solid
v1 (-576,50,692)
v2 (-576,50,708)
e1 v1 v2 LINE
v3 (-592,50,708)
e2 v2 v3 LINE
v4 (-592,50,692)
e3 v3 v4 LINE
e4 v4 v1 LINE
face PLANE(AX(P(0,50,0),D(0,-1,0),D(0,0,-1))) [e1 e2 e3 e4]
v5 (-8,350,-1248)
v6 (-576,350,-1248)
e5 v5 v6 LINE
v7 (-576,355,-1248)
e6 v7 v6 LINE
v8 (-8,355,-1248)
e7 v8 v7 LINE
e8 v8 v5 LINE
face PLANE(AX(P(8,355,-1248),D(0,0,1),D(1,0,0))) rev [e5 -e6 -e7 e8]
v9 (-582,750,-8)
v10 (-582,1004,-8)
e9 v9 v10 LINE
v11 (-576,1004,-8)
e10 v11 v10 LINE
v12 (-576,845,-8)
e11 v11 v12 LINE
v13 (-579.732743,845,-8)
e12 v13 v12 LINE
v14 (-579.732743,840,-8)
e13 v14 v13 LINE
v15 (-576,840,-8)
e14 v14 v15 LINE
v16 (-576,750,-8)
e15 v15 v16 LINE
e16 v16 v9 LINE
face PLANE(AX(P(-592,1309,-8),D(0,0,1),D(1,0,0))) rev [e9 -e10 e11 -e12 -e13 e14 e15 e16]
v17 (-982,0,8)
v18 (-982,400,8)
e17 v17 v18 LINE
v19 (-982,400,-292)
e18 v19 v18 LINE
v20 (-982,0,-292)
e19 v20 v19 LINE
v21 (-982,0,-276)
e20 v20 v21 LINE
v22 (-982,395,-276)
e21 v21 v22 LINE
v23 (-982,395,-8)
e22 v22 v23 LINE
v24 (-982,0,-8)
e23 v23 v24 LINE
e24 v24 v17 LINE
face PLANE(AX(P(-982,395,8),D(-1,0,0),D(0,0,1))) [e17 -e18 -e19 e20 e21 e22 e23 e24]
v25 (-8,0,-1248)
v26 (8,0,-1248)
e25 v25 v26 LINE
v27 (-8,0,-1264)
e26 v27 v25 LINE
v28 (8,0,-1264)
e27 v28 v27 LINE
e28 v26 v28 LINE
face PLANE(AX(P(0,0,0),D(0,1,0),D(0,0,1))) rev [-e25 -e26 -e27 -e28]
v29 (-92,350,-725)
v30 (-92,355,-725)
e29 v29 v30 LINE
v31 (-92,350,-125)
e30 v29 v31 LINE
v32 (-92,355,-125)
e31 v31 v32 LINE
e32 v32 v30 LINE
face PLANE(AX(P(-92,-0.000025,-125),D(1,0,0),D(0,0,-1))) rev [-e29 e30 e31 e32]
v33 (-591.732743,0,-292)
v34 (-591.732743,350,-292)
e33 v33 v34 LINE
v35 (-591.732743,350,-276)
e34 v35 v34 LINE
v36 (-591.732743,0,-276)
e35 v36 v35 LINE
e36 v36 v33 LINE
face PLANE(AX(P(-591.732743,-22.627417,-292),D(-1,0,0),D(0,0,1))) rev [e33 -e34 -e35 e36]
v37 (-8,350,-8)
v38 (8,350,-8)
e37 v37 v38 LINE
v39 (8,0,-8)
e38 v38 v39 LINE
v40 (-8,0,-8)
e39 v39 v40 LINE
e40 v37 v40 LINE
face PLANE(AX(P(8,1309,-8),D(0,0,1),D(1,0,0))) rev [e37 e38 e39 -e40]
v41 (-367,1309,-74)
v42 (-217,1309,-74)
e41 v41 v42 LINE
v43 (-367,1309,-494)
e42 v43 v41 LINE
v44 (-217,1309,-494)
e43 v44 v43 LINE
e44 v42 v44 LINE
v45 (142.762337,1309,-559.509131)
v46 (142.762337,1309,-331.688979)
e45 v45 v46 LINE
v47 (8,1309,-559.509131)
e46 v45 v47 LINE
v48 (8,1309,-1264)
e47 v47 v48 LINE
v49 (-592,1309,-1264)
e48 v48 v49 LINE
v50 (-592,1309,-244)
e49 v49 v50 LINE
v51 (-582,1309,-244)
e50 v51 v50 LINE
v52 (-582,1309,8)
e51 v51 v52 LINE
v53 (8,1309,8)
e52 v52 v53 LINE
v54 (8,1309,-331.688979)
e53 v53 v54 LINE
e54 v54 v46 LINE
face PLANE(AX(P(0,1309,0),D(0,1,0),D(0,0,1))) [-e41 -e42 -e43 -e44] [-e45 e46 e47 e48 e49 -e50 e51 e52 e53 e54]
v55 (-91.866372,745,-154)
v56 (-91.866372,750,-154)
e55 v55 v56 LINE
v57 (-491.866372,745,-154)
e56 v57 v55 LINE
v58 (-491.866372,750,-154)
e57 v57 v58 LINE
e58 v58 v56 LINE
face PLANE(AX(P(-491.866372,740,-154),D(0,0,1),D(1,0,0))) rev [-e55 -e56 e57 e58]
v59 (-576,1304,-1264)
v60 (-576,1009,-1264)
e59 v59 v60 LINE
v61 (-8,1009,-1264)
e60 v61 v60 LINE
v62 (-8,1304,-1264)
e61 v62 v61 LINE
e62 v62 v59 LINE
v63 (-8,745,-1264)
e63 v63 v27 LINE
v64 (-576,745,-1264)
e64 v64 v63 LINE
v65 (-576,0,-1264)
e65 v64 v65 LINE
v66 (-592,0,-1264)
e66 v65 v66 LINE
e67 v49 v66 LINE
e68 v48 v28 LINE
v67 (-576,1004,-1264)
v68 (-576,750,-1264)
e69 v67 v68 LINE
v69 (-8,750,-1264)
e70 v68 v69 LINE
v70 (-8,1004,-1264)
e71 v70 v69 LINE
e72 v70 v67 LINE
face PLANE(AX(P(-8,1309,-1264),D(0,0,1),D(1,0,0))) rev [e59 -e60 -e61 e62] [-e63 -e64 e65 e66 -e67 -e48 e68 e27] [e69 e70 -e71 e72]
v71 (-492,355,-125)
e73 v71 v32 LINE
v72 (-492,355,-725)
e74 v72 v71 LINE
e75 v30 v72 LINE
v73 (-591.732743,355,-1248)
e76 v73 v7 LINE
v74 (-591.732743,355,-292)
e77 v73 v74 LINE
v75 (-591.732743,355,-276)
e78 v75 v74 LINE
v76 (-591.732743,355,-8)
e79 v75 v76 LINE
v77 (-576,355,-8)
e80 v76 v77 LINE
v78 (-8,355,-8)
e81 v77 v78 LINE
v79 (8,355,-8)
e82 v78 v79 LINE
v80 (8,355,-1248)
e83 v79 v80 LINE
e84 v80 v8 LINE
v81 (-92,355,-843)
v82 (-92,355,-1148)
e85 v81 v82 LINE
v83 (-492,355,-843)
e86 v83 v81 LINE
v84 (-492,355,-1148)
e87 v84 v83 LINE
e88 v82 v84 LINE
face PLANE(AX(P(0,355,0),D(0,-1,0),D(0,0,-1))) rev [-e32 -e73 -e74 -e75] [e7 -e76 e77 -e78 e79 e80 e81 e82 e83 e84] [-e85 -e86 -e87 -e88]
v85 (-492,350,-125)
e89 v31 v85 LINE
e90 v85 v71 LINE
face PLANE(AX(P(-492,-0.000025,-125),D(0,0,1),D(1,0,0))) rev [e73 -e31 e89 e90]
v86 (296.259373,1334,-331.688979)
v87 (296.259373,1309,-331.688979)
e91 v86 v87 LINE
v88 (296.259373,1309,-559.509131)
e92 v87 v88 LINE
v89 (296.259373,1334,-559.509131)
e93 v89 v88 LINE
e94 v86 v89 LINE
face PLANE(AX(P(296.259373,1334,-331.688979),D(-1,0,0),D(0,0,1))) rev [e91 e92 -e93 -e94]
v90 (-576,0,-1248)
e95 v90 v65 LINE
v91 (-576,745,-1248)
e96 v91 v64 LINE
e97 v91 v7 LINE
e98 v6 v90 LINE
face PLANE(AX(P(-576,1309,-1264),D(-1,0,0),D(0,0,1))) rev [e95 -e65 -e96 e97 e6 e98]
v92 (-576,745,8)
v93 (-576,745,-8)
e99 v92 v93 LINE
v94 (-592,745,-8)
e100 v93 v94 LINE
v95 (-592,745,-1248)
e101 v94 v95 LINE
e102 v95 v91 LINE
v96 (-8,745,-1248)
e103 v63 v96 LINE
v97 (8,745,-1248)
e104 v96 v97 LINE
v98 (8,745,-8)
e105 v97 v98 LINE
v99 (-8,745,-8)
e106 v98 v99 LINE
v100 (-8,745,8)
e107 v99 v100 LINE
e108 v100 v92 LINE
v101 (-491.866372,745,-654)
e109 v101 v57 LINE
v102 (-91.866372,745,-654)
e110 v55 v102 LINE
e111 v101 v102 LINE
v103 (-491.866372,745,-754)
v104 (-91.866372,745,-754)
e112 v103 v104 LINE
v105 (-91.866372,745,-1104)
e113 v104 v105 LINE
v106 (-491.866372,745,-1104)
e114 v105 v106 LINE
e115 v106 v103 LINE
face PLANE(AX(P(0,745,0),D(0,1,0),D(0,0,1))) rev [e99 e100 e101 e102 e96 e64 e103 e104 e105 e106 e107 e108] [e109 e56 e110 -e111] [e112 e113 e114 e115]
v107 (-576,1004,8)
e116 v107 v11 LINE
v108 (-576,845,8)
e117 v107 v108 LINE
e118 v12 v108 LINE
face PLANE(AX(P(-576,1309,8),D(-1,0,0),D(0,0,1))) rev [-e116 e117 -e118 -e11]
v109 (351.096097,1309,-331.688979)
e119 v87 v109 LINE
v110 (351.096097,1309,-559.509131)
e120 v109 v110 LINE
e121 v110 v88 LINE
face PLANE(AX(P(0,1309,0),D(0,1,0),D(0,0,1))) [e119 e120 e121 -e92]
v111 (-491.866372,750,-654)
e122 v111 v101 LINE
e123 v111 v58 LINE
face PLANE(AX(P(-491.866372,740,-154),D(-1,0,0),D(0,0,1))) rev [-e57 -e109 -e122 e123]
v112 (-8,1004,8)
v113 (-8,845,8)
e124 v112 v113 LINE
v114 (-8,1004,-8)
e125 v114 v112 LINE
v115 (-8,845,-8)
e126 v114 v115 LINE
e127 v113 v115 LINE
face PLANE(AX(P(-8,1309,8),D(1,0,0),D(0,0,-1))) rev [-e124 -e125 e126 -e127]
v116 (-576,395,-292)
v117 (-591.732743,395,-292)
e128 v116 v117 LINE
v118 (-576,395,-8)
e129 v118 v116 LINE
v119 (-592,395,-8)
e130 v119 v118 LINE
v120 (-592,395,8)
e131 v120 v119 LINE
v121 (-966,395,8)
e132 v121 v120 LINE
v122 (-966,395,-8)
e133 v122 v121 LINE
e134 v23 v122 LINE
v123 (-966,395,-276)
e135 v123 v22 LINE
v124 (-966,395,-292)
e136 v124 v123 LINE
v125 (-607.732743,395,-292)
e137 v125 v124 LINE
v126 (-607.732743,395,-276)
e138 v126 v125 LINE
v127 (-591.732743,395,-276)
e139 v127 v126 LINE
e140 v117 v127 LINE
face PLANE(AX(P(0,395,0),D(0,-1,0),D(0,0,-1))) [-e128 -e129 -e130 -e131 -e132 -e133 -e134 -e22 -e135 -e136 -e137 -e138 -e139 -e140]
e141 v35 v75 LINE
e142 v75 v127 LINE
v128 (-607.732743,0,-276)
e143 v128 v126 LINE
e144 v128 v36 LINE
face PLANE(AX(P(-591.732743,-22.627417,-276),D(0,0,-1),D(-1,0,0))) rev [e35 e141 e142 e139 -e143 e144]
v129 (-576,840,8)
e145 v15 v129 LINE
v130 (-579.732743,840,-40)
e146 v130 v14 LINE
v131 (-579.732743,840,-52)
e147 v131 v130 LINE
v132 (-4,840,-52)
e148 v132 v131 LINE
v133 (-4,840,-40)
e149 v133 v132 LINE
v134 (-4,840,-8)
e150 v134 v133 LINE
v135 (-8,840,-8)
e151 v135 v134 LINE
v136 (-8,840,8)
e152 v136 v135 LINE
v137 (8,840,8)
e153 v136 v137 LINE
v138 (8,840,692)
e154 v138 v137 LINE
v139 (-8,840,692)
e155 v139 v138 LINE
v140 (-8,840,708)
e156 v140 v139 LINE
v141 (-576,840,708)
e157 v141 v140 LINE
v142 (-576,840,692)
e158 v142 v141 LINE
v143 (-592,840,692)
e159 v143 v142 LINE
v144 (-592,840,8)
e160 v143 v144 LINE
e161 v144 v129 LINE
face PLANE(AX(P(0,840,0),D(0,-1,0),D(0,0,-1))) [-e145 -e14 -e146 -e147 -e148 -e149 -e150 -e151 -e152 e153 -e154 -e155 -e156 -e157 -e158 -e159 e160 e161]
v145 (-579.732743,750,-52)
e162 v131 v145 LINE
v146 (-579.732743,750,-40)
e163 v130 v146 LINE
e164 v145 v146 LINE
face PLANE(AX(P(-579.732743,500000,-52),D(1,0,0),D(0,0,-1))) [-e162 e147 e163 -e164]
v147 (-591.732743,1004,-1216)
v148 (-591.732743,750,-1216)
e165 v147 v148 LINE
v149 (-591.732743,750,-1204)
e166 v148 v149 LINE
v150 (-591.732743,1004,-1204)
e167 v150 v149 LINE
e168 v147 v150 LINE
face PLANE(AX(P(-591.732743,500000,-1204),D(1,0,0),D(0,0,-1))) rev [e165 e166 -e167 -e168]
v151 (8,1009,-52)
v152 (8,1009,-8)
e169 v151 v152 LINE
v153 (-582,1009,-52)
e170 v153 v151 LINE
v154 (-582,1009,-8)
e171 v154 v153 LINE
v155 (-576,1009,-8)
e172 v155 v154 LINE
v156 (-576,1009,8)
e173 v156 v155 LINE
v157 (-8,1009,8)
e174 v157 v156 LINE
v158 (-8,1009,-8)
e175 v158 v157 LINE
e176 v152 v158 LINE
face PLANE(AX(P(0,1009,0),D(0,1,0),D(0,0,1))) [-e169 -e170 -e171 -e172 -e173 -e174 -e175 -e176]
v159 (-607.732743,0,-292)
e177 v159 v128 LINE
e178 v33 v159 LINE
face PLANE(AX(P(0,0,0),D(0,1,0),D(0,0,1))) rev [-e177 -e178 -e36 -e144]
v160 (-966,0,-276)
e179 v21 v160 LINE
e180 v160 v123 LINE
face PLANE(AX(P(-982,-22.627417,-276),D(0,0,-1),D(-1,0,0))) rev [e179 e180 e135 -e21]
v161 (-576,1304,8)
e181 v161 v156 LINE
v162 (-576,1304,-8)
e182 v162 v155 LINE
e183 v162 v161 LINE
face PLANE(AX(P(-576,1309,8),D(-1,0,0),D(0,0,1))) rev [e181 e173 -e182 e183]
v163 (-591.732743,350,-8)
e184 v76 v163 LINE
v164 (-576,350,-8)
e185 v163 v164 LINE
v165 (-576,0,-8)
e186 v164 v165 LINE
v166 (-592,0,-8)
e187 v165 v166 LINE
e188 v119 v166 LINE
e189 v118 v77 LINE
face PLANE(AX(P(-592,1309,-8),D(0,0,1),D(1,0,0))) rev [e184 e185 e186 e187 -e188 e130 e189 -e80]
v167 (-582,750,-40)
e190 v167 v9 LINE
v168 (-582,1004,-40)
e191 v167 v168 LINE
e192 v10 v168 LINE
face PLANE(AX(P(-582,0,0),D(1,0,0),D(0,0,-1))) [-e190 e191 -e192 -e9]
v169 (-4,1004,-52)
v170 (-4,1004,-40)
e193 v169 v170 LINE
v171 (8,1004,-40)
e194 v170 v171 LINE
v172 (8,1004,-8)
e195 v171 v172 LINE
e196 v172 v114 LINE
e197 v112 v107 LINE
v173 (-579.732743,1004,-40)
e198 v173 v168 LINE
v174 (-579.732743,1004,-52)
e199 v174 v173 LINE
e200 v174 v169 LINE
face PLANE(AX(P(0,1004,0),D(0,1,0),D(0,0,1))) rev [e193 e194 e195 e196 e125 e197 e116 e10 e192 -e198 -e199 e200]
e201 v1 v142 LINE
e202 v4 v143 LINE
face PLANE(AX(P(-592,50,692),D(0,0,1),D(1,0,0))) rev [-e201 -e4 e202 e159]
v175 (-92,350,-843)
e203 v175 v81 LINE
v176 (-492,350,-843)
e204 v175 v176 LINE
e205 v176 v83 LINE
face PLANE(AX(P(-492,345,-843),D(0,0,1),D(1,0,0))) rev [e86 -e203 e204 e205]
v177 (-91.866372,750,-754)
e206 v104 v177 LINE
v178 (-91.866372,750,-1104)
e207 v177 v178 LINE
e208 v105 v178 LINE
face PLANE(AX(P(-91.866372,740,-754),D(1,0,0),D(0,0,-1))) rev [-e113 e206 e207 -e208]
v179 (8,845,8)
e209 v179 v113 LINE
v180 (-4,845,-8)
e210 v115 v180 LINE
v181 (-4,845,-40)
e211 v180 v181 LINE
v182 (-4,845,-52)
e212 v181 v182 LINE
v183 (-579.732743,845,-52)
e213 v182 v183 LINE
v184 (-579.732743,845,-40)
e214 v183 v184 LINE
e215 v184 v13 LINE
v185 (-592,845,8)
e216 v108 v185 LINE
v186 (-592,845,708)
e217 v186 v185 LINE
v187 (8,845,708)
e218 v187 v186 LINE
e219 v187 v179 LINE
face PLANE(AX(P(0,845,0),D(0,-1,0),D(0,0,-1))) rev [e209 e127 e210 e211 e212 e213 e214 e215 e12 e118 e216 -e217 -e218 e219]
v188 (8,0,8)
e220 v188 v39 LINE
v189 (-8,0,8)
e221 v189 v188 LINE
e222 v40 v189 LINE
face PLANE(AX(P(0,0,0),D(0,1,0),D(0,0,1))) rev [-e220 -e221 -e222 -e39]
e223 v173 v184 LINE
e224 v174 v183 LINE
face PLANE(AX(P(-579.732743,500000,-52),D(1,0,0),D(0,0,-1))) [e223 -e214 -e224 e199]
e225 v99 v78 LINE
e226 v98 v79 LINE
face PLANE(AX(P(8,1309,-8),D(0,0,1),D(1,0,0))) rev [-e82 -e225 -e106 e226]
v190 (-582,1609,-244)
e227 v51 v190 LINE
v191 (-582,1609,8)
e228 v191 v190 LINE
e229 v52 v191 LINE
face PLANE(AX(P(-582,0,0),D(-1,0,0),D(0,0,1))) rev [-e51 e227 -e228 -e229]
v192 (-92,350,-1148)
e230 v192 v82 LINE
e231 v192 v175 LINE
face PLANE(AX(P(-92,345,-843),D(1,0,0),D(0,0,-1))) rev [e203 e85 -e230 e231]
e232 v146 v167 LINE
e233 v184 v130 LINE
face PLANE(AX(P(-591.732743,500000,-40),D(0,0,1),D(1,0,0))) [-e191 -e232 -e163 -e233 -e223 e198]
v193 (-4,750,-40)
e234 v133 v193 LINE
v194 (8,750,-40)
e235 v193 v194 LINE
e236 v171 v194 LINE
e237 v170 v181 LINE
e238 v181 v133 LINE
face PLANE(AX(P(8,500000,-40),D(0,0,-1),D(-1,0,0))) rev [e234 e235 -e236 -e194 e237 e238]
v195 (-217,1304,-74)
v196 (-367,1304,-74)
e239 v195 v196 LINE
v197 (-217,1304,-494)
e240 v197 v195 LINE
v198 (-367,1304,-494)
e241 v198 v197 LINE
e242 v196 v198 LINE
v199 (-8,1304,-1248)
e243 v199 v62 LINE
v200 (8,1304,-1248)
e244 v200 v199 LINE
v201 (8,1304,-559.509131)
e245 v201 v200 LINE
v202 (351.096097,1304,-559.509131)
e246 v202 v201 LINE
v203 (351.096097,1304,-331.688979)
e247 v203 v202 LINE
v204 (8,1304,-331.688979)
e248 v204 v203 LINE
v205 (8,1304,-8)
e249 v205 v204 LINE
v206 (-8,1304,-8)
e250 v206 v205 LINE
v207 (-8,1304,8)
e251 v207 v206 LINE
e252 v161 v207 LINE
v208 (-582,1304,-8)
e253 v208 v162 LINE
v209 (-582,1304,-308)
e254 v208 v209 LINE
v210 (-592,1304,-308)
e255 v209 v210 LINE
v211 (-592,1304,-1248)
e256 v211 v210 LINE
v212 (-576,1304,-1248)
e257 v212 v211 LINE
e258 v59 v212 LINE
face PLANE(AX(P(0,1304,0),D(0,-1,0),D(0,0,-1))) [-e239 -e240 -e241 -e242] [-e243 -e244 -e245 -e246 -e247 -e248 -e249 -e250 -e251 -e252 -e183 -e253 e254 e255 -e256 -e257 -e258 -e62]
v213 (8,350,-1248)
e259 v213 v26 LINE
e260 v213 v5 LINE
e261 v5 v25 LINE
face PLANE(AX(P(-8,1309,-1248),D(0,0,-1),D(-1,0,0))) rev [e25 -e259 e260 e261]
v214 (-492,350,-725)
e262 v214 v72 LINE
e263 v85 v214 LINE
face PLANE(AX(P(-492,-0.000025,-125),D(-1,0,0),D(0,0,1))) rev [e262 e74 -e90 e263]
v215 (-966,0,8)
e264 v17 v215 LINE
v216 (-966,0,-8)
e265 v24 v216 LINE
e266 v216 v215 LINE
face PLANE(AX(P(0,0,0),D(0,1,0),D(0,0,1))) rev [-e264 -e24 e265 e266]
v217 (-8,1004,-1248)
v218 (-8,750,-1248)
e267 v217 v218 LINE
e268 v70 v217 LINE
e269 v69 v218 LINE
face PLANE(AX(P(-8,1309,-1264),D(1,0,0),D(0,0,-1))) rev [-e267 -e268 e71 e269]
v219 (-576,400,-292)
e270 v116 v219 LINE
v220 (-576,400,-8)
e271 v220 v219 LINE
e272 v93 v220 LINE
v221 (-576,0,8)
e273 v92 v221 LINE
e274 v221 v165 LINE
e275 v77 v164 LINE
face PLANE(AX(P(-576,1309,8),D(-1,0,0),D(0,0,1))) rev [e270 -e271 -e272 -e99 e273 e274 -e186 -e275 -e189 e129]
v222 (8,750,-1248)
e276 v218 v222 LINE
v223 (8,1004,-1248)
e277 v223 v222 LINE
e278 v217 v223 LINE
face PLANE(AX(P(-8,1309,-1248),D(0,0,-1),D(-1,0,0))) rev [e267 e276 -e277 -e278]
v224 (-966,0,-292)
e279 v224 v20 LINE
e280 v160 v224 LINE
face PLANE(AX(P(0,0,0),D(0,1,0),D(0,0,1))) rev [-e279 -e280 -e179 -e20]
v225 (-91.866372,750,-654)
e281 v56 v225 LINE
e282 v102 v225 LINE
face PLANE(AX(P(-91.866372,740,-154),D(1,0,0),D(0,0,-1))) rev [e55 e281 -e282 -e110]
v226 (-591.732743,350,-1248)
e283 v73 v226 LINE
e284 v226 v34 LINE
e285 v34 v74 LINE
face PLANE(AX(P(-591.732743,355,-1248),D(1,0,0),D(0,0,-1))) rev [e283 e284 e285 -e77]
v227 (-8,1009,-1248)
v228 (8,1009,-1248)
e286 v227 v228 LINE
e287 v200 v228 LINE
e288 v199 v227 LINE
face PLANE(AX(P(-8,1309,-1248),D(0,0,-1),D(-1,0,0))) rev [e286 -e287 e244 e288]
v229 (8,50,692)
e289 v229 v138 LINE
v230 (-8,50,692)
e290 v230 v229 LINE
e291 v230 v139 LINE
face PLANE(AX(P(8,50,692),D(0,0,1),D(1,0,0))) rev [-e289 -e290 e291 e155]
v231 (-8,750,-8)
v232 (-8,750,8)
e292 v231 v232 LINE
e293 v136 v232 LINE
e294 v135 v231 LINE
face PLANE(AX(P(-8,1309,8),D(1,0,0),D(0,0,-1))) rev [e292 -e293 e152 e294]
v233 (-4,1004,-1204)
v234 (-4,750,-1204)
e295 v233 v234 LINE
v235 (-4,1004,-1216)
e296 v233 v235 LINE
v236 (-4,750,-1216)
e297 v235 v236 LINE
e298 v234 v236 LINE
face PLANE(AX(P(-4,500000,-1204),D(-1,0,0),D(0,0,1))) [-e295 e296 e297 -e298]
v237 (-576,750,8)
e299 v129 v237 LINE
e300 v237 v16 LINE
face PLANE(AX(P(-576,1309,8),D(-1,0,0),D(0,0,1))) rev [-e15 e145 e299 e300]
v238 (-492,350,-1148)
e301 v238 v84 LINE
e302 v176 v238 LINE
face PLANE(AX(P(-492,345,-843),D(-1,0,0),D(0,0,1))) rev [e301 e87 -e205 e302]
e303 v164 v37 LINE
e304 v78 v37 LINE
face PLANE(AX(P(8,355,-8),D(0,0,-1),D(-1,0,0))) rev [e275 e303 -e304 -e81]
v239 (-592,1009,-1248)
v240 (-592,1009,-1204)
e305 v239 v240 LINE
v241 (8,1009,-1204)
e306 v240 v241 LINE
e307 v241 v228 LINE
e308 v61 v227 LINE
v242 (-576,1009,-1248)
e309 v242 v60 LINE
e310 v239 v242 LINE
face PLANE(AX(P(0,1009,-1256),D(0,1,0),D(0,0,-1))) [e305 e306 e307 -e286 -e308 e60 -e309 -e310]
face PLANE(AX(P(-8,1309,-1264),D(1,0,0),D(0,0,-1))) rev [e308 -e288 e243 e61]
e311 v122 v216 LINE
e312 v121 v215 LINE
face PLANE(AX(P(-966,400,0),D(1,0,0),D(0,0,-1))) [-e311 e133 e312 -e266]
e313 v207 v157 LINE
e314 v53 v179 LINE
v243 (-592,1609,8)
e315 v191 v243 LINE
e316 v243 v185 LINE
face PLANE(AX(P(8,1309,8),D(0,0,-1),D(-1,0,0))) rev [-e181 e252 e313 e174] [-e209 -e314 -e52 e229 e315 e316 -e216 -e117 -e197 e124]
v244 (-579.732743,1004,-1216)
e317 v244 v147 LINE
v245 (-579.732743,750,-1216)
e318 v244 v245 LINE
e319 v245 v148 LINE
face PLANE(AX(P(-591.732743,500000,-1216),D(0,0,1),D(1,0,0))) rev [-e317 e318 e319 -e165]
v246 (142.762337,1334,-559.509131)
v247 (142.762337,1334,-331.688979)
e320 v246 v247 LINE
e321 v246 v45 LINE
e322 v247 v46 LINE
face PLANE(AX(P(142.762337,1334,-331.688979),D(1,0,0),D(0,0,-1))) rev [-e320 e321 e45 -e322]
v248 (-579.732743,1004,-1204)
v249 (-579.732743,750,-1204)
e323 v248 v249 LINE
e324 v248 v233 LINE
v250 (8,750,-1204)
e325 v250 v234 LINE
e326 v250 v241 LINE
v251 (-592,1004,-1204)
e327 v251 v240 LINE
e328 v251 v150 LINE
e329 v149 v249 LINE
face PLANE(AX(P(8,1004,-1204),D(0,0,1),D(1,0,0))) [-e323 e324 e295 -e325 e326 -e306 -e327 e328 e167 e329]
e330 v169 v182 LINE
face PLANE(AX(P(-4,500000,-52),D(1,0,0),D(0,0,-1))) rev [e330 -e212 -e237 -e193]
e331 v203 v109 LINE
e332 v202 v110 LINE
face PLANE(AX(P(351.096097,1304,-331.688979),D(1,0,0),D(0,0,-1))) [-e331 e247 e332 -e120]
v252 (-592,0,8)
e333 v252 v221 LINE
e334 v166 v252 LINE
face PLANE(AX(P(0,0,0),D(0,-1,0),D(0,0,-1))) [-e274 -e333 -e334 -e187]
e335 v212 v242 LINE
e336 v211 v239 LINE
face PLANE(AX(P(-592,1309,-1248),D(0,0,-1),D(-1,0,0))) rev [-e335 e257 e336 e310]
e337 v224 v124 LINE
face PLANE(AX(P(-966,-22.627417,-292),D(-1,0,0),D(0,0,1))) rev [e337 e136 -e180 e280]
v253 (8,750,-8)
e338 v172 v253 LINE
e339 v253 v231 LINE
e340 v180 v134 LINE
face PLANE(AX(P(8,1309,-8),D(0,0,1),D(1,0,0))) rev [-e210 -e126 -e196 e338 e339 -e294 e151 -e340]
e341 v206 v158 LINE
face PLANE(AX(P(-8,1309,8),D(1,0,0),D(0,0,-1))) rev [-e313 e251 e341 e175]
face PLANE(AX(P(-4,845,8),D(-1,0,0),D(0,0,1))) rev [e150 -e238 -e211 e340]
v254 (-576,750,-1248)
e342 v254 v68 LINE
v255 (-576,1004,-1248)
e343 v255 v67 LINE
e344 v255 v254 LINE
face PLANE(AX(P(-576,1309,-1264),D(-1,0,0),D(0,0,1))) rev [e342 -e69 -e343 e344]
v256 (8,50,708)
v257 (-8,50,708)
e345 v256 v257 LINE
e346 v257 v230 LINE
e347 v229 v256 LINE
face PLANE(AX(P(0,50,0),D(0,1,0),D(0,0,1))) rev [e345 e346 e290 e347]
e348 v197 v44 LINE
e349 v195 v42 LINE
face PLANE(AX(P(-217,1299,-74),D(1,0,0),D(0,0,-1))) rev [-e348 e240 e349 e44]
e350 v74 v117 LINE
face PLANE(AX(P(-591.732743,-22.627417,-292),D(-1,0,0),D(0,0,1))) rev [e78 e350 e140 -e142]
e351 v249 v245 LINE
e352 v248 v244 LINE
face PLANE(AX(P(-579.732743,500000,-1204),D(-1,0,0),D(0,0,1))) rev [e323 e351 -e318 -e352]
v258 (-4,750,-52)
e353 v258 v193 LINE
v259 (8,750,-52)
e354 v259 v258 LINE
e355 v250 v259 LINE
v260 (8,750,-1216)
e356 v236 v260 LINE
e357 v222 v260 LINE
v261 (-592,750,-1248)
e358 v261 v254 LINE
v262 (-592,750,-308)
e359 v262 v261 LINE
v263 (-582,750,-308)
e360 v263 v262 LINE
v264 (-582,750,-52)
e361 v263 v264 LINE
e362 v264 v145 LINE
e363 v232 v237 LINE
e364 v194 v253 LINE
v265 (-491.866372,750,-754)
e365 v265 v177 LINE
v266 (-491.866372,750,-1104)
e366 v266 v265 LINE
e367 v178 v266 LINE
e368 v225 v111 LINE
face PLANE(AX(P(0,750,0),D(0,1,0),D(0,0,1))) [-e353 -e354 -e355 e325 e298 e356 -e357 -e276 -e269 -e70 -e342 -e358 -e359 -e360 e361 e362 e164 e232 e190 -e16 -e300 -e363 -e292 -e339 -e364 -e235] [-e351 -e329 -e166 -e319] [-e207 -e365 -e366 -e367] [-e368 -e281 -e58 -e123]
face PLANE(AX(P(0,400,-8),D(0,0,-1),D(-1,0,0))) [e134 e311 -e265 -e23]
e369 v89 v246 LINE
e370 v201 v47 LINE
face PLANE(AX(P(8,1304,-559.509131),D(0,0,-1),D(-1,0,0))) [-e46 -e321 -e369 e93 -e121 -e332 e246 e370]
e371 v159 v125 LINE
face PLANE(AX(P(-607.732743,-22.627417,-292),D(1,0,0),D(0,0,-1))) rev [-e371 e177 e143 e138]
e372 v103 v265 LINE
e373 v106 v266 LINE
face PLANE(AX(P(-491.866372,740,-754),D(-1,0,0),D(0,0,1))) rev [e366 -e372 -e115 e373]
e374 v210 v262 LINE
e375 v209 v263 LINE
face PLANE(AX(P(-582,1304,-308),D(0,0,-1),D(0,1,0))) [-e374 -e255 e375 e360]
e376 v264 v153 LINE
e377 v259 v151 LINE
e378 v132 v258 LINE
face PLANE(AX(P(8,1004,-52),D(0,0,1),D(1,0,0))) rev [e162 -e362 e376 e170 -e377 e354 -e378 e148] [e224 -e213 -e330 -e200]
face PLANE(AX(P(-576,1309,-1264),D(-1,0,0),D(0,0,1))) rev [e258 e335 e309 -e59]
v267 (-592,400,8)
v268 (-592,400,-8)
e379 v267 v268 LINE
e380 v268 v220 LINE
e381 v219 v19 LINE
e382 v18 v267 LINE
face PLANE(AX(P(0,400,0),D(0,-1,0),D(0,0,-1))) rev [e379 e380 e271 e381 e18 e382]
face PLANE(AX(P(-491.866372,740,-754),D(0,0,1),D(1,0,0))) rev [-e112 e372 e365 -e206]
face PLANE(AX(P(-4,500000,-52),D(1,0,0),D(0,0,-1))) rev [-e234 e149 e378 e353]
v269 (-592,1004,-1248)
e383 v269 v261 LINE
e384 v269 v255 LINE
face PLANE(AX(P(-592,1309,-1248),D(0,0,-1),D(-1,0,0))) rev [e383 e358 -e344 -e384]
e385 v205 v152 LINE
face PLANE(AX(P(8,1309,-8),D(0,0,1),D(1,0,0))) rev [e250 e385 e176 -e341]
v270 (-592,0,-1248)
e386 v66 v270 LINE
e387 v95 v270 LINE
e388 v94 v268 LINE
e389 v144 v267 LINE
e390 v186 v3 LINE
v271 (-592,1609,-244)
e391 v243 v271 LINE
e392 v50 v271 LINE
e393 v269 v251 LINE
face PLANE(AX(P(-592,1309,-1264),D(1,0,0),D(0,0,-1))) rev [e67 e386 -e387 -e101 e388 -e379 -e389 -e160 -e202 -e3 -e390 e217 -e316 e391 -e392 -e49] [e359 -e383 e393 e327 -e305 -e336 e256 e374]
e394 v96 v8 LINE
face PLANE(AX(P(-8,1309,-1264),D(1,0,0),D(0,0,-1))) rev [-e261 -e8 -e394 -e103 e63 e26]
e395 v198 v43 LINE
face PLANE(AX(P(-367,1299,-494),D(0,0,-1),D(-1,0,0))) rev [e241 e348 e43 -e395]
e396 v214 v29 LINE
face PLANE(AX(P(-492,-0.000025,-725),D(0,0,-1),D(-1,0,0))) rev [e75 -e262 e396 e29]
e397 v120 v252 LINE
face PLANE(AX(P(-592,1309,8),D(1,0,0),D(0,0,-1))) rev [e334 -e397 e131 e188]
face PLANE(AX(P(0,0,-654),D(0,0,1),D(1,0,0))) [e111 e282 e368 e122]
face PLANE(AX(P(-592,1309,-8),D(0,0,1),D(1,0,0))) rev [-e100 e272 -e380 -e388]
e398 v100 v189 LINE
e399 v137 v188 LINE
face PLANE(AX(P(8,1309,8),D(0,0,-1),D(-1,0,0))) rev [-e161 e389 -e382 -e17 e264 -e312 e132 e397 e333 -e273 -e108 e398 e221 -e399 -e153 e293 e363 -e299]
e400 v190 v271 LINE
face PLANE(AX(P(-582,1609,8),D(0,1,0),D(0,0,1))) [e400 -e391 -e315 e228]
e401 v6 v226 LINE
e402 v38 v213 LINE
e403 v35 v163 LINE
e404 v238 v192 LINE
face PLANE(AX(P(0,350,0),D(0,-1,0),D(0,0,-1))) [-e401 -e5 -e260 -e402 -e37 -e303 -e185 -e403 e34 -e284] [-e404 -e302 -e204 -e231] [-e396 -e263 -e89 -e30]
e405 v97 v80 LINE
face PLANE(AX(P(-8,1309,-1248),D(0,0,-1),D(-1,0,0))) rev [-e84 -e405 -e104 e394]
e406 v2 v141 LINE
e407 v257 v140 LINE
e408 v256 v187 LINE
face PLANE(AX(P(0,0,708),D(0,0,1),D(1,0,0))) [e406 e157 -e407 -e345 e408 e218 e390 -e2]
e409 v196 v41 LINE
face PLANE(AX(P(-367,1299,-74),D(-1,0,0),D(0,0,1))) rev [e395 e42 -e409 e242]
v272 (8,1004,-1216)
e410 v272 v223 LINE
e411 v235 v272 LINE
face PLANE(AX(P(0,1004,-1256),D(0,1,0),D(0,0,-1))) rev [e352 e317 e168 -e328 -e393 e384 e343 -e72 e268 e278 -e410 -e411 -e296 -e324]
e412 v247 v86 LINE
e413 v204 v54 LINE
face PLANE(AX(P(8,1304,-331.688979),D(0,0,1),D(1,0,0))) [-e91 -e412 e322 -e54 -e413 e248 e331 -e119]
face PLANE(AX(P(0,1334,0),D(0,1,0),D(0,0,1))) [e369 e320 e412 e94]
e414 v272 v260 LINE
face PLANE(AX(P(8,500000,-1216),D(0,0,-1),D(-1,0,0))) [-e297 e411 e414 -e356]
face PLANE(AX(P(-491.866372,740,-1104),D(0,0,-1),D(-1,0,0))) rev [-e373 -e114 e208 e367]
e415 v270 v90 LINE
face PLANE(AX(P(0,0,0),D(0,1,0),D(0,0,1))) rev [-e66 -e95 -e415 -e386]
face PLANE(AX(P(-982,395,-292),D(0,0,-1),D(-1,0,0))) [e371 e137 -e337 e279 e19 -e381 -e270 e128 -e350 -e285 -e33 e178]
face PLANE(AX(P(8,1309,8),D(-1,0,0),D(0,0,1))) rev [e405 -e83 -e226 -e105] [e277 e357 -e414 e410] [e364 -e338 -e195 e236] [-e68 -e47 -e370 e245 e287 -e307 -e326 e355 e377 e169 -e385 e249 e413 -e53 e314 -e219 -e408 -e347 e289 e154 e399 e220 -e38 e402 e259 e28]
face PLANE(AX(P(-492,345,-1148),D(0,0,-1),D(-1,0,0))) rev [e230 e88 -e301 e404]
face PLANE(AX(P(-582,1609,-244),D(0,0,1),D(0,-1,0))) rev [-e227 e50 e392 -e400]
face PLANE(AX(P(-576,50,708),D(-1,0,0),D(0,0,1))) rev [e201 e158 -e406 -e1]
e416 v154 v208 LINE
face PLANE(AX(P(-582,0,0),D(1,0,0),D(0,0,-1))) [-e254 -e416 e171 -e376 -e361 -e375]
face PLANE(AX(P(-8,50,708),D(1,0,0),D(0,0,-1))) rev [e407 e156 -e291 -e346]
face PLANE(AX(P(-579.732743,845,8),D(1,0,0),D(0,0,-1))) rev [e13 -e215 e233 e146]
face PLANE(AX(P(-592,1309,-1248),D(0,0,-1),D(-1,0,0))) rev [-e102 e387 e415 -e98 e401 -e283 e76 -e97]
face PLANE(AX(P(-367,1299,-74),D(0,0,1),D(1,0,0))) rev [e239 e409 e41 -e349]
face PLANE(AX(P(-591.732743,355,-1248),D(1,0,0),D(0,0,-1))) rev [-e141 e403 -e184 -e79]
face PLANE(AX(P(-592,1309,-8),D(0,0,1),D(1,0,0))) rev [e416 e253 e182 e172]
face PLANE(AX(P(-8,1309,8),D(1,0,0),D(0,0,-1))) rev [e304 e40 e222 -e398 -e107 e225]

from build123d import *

# Parameters (mm, degrees)
SKETCH_4_W               = 16
SKETCH_4_H               = 16
EXTRUDE_1_DEPTH          = 1309
EXTRUDE_1_2_DEPTH        = 1309
EXTRUDE_1_3_DEPTH        = 1309
EXTRUDE_1_4_DEPTH        = 1309
SKETCH_5_W               = 599.732743224
SKETCH_5_H               = 1240
EXTRUDE_2_DEPTH          = 5
SKETCH_7_W               = 16
SKETCH_7_H               = 16
EXTRUDE_3_DEPTH          = 400
SKETCH_8_W               = 406
SKETCH_8_H               = 300
EXTRUDE_4_DEPTH          = 5
SKETCH_9_W               = 600
SKETCH_9_H               = 1272
EXTRUDE_5_DEPTH          = 5
SKETCH_10_W              = 600
SKETCH_10_H              = 60
EXTRUDE_6_DEPTH          = 5
EXTRUDE_7_REACH          = 1769.631
SKETCH_11_W              = 12
SKETCH_11_H              = 12
MIRROR_3_COPY_1_REACH    = 1769.631
MIRROR_3_COPY_1_SKETCH_W = 12
MIRROR_3_COPY_1_SKETCH_H = 12
SKETCH_12_W              = 600
SKETCH_12_H              = 1272
EXTRUDE_8_DEPTH          = 5
EXTRUDE_START            = 90
SKETCH_18_W              = 575.732743224
SKETCH_18_H              = 60
EXTRUDE_11_DEPTH         = 5
SKETCH_19_W              = 600
SKETCH_19_H              = 5
EXTRUDE_12_DEPTH         = 700
SKETCH_21_W              = 400
SKETCH_21_H              = 350
CUT_EXTRUDE_4_DEPTH      = 10
SKETCH_22_W              = 16
SKETCH_22_H              = 16
EXTRUDE_14_DEPTH         = 790
SKETCH_23_W              = 400
SKETCH_23_H              = 600
CUT_EXTRUDE_5_DEPTH      = 1864.366845256
SKETCH_24_W              = 150
SKETCH_24_H              = 420
CUT_EXTRUDE_6_DEPTH      = 10
SKETCH_25_W              = 400
SKETCH_25_H              = 305
CUT_EXTRUDE_7_DEPTH      = 10
EXTRUDE_15_REACH         = 1845.208
SKETCH_26_W              = 16
SKETCH_26_H              = 16
PATTERN_LINEAR_1_COUNT   = 2
PATTERN_LINEAR_1_PITCH   = 600
SKETCH_27_W              = 400
SKETCH_27_H              = 5
CUT_EXTRUDE_8_DEPTH      = 150
SKETCH_28_W              = 300
SKETCH_28_H              = 554
EXTRUDE_16_DEPTH         = 10
SKETCH_29_W              = 316
SKETCH_29_H              = 300
EXTRUDE_17_DEPTH         = 10
SKETCH_30_W              = 64
SKETCH_30_H              = 300
CUT_EXTRUDE_9_DEPTH      = 10
SKETCH_35_W              = 343.096096547
SKETCH_35_H              = 227.820151314
EXTRUDE_18_DEPTH         = 5
SKETCH_36_W              = 153.4970354
SKETCH_36_H              = 227.820151314
EXTRUDE_19_DEPTH         = 25


with BuildPart() as part:
    # 草图4 → 凸台-拉伸1 (new body)
    with BuildSketch(Plane(origin=(0, 0, 0), x_dir=(1, 0, 0), z_dir=(0, 1, 0))):
        Rectangle(SKETCH_4_W, SKETCH_4_H)
    extrude(amount=EXTRUDE_1_DEPTH)



with BuildPart() as body_2:
    # 草图4 → Extrude 1 2 (new body)
    with BuildSketch(Plane(origin=(0, 0, 0), x_dir=(1, 0, 0), z_dir=(0, 1, 0))):
        with Locations((0, 1256)):
            Rectangle(SKETCH_4_W, SKETCH_4_H)
    extrude(amount=EXTRUDE_1_2_DEPTH)


with BuildPart() as body_3:
    # 草图4 → Extrude 1 3 (new body)
    with BuildSketch(Plane(origin=(0, 0, 0), x_dir=(1, 0, 0), z_dir=(0, 1, 0))):
        with Locations((-584, 0)):
            Rectangle(SKETCH_4_W, SKETCH_4_H)
    extrude(amount=EXTRUDE_1_3_DEPTH)


with BuildPart() as body_4:
    # 草图4 → Extrude 1 4 (new body)
    with BuildSketch(Plane(origin=(0, 0, 0), x_dir=(1, 0, 0), z_dir=(0, 1, 0))):
        with Locations((-584, 1256)):
            Rectangle(SKETCH_4_W, SKETCH_4_H)
    extrude(amount=EXTRUDE_1_4_DEPTH)


with BuildPart() as part_1:
    add(part.part)

    add(body_2.part)  # 凸台-拉伸2 merges body 2

    add(body_3.part)  # 凸台-拉伸2 merges body 3

    add(body_4.part)  # 凸台-拉伸2 merges body 4
    # 草图5 → 凸台-拉伸2 (add)
    with BuildSketch(Plane(origin=(0, 350, 0), x_dir=(1, 0, 0), z_dir=(0, 1, 0))):
        with Locations((-291.866371612, 628)):
            Rectangle(SKETCH_5_W, SKETCH_5_H)
    extrude(amount=EXTRUDE_2_DEPTH)



with BuildPart() as body_2_2:
    # 草图7 → 凸台-拉伸3 (new body)
    with BuildSketch(Plane(origin=(0, 0, 0), x_dir=(1, 0, 0), z_dir=(0, 1, 0))):
        with Locations((-974, 0)):
            Rectangle(SKETCH_7_W, SKETCH_7_H)
    extrude(amount=EXTRUDE_3_DEPTH)


with BuildPart() as part_2:
    add(part_1.part)

    add(body_2_2.part)  # 凸台-拉伸4 merges body 2 2
    # 草图8 → 凸台-拉伸4 (add)
    with BuildSketch(Plane(origin=(0, 400, 0), x_dir=(1, 0, 0), z_dir=(0, 1, 0))):
        with Locations((-779, 142)):
            Rectangle(SKETCH_8_W, SKETCH_8_H)
    extrude(amount=-EXTRUDE_4_DEPTH)

    # 草图9 → 凸台-拉伸5 (add)
    with BuildSketch(Plane(origin=(0, 750, 0), x_dir=(-1, 0, 0), z_dir=(0, -1, 0))):
        with Locations((292, 628)):
            Rectangle(SKETCH_9_W, SKETCH_9_H)
    extrude(amount=EXTRUDE_5_DEPTH)

    # 草图10 → 凸台-拉伸6 (add)
    with BuildSketch(Plane(origin=(0, 1009, 0), x_dir=(-1, 0, 0), z_dir=(0, -1, 0))):
        with Locations((292, 22)):
            Rectangle(SKETCH_10_W, SKETCH_10_H)
    extrude_6 = extrude(amount=EXTRUDE_6_DEPTH)

    # 镜向1: 凸台-拉伸6 across plane
    add(extrude_6.mirror(Plane.XY.offset(-628)))

    # 草图11 → 凸台-拉伸7 (add, up to next)
    with BuildSketch(Plane(origin=(0, 750, 0), x_dir=(1, 0, 0), z_dir=(0, 1, 0)), mode=Mode.PRIVATE) as extrude_7_sk1:
        with Locations((2, 46)):
            Rectangle(SKETCH_11_W, SKETCH_11_H)
    extrude_7_tool1 = extrude(extrude_7_sk1.sketch, amount=EXTRUDE_7_REACH, mode=Mode.PRIVATE) - part_2.part
    extrude_7 = extrude_7_tool1.solids().sort_by_distance((2, 750, -46))[0]
    add(extrude_7)

    # 镜向2: 凸台-拉伸7 across plane
    add(extrude_7.mirror(Plane(origin=(-291.866371612, 0, 0), x_dir=(0, 0, 1), z_dir=(1, 0, 0))))

    # 镜向3: 凸台-拉伸7 across plane
    add(extrude_7.mirror(Plane.XY.offset(-628)))

    # 镜向3 copy 1 sketch → 镜向3 copy 1 (add, up to next)
    with BuildSketch(Plane(origin=(-583.732743224, 750, -1256), x_dir=(-1, 0, 0), z_dir=(0, 1, 0)), mode=Mode.PRIVATE) as mirror_3_copy_1_sk1:
        with Locations((2, 46)):
            Rectangle(MIRROR_3_COPY_1_SKETCH_W, MIRROR_3_COPY_1_SKETCH_H)
    mirror_3_copy_1_tool1 = extrude(mirror_3_copy_1_sk1.sketch, amount=MIRROR_3_COPY_1_REACH, mode=Mode.PRIVATE) - part_2.part
    add(mirror_3_copy_1_tool1.solids().sort_by_distance((-585.732743224, 750, -1210))[0])

    # 草图12 → 凸台-拉伸8 (add)
    with BuildSketch(Plane(origin=(0, 1309, 0), x_dir=(1, 0, 0), z_dir=(0, 1, 0))):
        with Locations((-292, 628)):
            Rectangle(SKETCH_12_W, SKETCH_12_H)
    extrude(amount=-EXTRUDE_8_DEPTH)

    # 草图18 → 凸台-拉伸11 (add)
    with BuildSketch(Plane(origin=(0, 750, 0), x_dir=(1, 0, 0), z_dir=(0, 1, 0)).offset(EXTRUDE_START)):
        with Locations((-291.866371612, 22)):
            Rectangle(SKETCH_18_W, SKETCH_18_H)
    extrude(amount=EXTRUDE_11_DEPTH)

    # 草图19 → 凸台-拉伸12 (add)
    with BuildSketch(Plane.XY.offset(8)):
        with Locations((-292, 842.5)):
            Rectangle(SKETCH_19_W, SKETCH_19_H)
    extrude(amount=EXTRUDE_12_DEPTH)

    # 草图21 → 切除-拉伸4 (cut)
    with BuildSketch(Plane(origin=(0, 750, 0), x_dir=(1, 0, 0), z_dir=(0, 1, 0))):
        with Locations((-291.866371612, 929)):
            Rectangle(SKETCH_21_W, SKETCH_21_H)
    cut_extrude_4 = extrude(amount=-CUT_EXTRUDE_4_DEPTH, mode=Mode.SUBTRACT)

    # 草图22 → 凸台-拉伸14 (add)
    with BuildSketch(Plane.XZ.offset(-840)):
        with Locations((-584, 700)):
            Rectangle(SKETCH_22_W, SKETCH_22_H)
        with Locations((0, 700)):
            Rectangle(SKETCH_22_W, SKETCH_22_H)
    extrude(amount=EXTRUDE_14_DEPTH)

    # 草图23 → 切除-拉伸5 (cut, through all)
    with BuildSketch(Plane(origin=(0, 355, 0), x_dir=(1, 0, 0), z_dir=(0, 1, 0))):
        with Locations((-292, 425)):
            Rectangle(SKETCH_23_W, SKETCH_23_H)
    extrude(amount=-CUT_EXTRUDE_5_DEPTH, mode=Mode.SUBTRACT)

    # 草图24 → 切除-拉伸6 (cut)
    with BuildSketch(Plane(origin=(0, 1309, 0), x_dir=(1, 0, 0), z_dir=(0, 1, 0))):
        with Locations((-292, 284)):
            Rectangle(SKETCH_24_W, SKETCH_24_H)
    extrude(amount=-CUT_EXTRUDE_6_DEPTH, mode=Mode.SUBTRACT)

    # 草图25 → 切除-拉伸7 (cut)
    with BuildSketch(Plane(origin=(0, 355, 0), x_dir=(1, 0, 0), z_dir=(0, 1, 0))):
        with Locations((-292, 995.5)):
            Rectangle(SKETCH_25_W, SKETCH_25_H)
    extrude(amount=-CUT_EXTRUDE_7_DEPTH, mode=Mode.SUBTRACT)

    # 凸台-拉伸15: up to this face of the body (flat: up to its plane)
    extrude_15_end = Plane(part_2.part.faces().sort_by_distance((-974, 0, 0))[0])
    # 草图26 → 凸台-拉伸15 (add, up to the picked face)
    with BuildSketch(Plane.XZ.offset(-395), mode=Mode.PRIVATE) as extrude_15_sk1:
        with Locations((-974, -284)):
            Rectangle(SKETCH_26_W, SKETCH_26_H)
    extrude_15_tool1 = split(extrude(extrude_15_sk1.sketch, amount=EXTRUDE_15_REACH, mode=Mode.PRIVATE), bisect_by=extrude_15_end, keep=Keep.BOTH, mode=Mode.PRIVATE)
    # 草图26 → 凸台-拉伸15 (add, up to the picked face)
    with BuildSketch(Plane.XZ.offset(-395), mode=Mode.PRIVATE) as extrude_15_sk2:
        with Locations((-599.732743224, -284)):
            Rectangle(SKETCH_26_W, SKETCH_26_H)
    extrude_15_tool2 = split(extrude(extrude_15_sk2.sketch, amount=EXTRUDE_15_REACH, mode=Mode.PRIVATE), bisect_by=extrude_15_end, keep=Keep.BOTH, mode=Mode.PRIVATE)
    add(extrude_15_tool1.solids().sort_by(Axis((-974, 395, -284), (0, -1, 0)))[0])
    add(extrude_15_tool2.solids().sort_by(Axis((-599.732743, 395, -284), (0, -1, 0)))[0])

    # 阵列(线性)1: 切除-拉伸4 ×2
    with Locations(*[(0, 0, i * PATTERN_LINEAR_1_PITCH) for i in range(1, PATTERN_LINEAR_1_COUNT)]):
        add(cut_extrude_4, mode=Mode.SUBTRACT)

    # 草图27 → 切除-拉伸8 (cut)
    with BuildSketch(Plane.XY.offset(-504)):
        with Locations((-291.866371612, 747.5)):
            Rectangle(SKETCH_27_W, SKETCH_27_H)
    extrude(amount=-CUT_EXTRUDE_8_DEPTH, mode=Mode.SUBTRACT)

    # 草图28 → 凸台-拉伸16 (add)
    with BuildSketch(Plane.ZY.offset(592)):
        with Locations((-158, 1027)):
            Rectangle(SKETCH_28_W, SKETCH_28_H)
    extrude(amount=-EXTRUDE_16_DEPTH)

    # 草图29 → 凸台-拉伸17 (add)
    with BuildSketch(Plane.ZY.offset(592)):
        with Locations((-150, 1459)):
            Rectangle(SKETCH_29_W, SKETCH_29_H)
    extrude(amount=-EXTRUDE_17_DEPTH)

    # 草图30 → 切除-拉伸9 (cut)
    with BuildSketch(Plane.ZY.offset(592)):
        with Locations((-276, 1459)):
            Rectangle(SKETCH_30_W, SKETCH_30_H)
    extrude(amount=-CUT_EXTRUDE_9_DEPTH, mode=Mode.SUBTRACT)

    # 草图35 → 凸台-拉伸18 (add)
    with BuildSketch(Plane(origin=(0, 1309, 0), x_dir=(1, 0, 0), z_dir=(0, 1, 0))):
        with Locations((179.548048274, 445.599054932)):
            Rectangle(SKETCH_35_W, SKETCH_35_H)
    extrude(amount=-EXTRUDE_18_DEPTH)

    # 草图36 → 凸台-拉伸19 (add)
    with BuildSketch(Plane(origin=(0, 1309, 0), x_dir=(1, 0, 0), z_dir=(0, 1, 0))):
        with Locations((219.510855053, 445.599054932)):
            Rectangle(SKETCH_36_W, SKETCH_36_H)
    extrude(amount=EXTRUDE_19_DEPTH)


solid = part_2.part
